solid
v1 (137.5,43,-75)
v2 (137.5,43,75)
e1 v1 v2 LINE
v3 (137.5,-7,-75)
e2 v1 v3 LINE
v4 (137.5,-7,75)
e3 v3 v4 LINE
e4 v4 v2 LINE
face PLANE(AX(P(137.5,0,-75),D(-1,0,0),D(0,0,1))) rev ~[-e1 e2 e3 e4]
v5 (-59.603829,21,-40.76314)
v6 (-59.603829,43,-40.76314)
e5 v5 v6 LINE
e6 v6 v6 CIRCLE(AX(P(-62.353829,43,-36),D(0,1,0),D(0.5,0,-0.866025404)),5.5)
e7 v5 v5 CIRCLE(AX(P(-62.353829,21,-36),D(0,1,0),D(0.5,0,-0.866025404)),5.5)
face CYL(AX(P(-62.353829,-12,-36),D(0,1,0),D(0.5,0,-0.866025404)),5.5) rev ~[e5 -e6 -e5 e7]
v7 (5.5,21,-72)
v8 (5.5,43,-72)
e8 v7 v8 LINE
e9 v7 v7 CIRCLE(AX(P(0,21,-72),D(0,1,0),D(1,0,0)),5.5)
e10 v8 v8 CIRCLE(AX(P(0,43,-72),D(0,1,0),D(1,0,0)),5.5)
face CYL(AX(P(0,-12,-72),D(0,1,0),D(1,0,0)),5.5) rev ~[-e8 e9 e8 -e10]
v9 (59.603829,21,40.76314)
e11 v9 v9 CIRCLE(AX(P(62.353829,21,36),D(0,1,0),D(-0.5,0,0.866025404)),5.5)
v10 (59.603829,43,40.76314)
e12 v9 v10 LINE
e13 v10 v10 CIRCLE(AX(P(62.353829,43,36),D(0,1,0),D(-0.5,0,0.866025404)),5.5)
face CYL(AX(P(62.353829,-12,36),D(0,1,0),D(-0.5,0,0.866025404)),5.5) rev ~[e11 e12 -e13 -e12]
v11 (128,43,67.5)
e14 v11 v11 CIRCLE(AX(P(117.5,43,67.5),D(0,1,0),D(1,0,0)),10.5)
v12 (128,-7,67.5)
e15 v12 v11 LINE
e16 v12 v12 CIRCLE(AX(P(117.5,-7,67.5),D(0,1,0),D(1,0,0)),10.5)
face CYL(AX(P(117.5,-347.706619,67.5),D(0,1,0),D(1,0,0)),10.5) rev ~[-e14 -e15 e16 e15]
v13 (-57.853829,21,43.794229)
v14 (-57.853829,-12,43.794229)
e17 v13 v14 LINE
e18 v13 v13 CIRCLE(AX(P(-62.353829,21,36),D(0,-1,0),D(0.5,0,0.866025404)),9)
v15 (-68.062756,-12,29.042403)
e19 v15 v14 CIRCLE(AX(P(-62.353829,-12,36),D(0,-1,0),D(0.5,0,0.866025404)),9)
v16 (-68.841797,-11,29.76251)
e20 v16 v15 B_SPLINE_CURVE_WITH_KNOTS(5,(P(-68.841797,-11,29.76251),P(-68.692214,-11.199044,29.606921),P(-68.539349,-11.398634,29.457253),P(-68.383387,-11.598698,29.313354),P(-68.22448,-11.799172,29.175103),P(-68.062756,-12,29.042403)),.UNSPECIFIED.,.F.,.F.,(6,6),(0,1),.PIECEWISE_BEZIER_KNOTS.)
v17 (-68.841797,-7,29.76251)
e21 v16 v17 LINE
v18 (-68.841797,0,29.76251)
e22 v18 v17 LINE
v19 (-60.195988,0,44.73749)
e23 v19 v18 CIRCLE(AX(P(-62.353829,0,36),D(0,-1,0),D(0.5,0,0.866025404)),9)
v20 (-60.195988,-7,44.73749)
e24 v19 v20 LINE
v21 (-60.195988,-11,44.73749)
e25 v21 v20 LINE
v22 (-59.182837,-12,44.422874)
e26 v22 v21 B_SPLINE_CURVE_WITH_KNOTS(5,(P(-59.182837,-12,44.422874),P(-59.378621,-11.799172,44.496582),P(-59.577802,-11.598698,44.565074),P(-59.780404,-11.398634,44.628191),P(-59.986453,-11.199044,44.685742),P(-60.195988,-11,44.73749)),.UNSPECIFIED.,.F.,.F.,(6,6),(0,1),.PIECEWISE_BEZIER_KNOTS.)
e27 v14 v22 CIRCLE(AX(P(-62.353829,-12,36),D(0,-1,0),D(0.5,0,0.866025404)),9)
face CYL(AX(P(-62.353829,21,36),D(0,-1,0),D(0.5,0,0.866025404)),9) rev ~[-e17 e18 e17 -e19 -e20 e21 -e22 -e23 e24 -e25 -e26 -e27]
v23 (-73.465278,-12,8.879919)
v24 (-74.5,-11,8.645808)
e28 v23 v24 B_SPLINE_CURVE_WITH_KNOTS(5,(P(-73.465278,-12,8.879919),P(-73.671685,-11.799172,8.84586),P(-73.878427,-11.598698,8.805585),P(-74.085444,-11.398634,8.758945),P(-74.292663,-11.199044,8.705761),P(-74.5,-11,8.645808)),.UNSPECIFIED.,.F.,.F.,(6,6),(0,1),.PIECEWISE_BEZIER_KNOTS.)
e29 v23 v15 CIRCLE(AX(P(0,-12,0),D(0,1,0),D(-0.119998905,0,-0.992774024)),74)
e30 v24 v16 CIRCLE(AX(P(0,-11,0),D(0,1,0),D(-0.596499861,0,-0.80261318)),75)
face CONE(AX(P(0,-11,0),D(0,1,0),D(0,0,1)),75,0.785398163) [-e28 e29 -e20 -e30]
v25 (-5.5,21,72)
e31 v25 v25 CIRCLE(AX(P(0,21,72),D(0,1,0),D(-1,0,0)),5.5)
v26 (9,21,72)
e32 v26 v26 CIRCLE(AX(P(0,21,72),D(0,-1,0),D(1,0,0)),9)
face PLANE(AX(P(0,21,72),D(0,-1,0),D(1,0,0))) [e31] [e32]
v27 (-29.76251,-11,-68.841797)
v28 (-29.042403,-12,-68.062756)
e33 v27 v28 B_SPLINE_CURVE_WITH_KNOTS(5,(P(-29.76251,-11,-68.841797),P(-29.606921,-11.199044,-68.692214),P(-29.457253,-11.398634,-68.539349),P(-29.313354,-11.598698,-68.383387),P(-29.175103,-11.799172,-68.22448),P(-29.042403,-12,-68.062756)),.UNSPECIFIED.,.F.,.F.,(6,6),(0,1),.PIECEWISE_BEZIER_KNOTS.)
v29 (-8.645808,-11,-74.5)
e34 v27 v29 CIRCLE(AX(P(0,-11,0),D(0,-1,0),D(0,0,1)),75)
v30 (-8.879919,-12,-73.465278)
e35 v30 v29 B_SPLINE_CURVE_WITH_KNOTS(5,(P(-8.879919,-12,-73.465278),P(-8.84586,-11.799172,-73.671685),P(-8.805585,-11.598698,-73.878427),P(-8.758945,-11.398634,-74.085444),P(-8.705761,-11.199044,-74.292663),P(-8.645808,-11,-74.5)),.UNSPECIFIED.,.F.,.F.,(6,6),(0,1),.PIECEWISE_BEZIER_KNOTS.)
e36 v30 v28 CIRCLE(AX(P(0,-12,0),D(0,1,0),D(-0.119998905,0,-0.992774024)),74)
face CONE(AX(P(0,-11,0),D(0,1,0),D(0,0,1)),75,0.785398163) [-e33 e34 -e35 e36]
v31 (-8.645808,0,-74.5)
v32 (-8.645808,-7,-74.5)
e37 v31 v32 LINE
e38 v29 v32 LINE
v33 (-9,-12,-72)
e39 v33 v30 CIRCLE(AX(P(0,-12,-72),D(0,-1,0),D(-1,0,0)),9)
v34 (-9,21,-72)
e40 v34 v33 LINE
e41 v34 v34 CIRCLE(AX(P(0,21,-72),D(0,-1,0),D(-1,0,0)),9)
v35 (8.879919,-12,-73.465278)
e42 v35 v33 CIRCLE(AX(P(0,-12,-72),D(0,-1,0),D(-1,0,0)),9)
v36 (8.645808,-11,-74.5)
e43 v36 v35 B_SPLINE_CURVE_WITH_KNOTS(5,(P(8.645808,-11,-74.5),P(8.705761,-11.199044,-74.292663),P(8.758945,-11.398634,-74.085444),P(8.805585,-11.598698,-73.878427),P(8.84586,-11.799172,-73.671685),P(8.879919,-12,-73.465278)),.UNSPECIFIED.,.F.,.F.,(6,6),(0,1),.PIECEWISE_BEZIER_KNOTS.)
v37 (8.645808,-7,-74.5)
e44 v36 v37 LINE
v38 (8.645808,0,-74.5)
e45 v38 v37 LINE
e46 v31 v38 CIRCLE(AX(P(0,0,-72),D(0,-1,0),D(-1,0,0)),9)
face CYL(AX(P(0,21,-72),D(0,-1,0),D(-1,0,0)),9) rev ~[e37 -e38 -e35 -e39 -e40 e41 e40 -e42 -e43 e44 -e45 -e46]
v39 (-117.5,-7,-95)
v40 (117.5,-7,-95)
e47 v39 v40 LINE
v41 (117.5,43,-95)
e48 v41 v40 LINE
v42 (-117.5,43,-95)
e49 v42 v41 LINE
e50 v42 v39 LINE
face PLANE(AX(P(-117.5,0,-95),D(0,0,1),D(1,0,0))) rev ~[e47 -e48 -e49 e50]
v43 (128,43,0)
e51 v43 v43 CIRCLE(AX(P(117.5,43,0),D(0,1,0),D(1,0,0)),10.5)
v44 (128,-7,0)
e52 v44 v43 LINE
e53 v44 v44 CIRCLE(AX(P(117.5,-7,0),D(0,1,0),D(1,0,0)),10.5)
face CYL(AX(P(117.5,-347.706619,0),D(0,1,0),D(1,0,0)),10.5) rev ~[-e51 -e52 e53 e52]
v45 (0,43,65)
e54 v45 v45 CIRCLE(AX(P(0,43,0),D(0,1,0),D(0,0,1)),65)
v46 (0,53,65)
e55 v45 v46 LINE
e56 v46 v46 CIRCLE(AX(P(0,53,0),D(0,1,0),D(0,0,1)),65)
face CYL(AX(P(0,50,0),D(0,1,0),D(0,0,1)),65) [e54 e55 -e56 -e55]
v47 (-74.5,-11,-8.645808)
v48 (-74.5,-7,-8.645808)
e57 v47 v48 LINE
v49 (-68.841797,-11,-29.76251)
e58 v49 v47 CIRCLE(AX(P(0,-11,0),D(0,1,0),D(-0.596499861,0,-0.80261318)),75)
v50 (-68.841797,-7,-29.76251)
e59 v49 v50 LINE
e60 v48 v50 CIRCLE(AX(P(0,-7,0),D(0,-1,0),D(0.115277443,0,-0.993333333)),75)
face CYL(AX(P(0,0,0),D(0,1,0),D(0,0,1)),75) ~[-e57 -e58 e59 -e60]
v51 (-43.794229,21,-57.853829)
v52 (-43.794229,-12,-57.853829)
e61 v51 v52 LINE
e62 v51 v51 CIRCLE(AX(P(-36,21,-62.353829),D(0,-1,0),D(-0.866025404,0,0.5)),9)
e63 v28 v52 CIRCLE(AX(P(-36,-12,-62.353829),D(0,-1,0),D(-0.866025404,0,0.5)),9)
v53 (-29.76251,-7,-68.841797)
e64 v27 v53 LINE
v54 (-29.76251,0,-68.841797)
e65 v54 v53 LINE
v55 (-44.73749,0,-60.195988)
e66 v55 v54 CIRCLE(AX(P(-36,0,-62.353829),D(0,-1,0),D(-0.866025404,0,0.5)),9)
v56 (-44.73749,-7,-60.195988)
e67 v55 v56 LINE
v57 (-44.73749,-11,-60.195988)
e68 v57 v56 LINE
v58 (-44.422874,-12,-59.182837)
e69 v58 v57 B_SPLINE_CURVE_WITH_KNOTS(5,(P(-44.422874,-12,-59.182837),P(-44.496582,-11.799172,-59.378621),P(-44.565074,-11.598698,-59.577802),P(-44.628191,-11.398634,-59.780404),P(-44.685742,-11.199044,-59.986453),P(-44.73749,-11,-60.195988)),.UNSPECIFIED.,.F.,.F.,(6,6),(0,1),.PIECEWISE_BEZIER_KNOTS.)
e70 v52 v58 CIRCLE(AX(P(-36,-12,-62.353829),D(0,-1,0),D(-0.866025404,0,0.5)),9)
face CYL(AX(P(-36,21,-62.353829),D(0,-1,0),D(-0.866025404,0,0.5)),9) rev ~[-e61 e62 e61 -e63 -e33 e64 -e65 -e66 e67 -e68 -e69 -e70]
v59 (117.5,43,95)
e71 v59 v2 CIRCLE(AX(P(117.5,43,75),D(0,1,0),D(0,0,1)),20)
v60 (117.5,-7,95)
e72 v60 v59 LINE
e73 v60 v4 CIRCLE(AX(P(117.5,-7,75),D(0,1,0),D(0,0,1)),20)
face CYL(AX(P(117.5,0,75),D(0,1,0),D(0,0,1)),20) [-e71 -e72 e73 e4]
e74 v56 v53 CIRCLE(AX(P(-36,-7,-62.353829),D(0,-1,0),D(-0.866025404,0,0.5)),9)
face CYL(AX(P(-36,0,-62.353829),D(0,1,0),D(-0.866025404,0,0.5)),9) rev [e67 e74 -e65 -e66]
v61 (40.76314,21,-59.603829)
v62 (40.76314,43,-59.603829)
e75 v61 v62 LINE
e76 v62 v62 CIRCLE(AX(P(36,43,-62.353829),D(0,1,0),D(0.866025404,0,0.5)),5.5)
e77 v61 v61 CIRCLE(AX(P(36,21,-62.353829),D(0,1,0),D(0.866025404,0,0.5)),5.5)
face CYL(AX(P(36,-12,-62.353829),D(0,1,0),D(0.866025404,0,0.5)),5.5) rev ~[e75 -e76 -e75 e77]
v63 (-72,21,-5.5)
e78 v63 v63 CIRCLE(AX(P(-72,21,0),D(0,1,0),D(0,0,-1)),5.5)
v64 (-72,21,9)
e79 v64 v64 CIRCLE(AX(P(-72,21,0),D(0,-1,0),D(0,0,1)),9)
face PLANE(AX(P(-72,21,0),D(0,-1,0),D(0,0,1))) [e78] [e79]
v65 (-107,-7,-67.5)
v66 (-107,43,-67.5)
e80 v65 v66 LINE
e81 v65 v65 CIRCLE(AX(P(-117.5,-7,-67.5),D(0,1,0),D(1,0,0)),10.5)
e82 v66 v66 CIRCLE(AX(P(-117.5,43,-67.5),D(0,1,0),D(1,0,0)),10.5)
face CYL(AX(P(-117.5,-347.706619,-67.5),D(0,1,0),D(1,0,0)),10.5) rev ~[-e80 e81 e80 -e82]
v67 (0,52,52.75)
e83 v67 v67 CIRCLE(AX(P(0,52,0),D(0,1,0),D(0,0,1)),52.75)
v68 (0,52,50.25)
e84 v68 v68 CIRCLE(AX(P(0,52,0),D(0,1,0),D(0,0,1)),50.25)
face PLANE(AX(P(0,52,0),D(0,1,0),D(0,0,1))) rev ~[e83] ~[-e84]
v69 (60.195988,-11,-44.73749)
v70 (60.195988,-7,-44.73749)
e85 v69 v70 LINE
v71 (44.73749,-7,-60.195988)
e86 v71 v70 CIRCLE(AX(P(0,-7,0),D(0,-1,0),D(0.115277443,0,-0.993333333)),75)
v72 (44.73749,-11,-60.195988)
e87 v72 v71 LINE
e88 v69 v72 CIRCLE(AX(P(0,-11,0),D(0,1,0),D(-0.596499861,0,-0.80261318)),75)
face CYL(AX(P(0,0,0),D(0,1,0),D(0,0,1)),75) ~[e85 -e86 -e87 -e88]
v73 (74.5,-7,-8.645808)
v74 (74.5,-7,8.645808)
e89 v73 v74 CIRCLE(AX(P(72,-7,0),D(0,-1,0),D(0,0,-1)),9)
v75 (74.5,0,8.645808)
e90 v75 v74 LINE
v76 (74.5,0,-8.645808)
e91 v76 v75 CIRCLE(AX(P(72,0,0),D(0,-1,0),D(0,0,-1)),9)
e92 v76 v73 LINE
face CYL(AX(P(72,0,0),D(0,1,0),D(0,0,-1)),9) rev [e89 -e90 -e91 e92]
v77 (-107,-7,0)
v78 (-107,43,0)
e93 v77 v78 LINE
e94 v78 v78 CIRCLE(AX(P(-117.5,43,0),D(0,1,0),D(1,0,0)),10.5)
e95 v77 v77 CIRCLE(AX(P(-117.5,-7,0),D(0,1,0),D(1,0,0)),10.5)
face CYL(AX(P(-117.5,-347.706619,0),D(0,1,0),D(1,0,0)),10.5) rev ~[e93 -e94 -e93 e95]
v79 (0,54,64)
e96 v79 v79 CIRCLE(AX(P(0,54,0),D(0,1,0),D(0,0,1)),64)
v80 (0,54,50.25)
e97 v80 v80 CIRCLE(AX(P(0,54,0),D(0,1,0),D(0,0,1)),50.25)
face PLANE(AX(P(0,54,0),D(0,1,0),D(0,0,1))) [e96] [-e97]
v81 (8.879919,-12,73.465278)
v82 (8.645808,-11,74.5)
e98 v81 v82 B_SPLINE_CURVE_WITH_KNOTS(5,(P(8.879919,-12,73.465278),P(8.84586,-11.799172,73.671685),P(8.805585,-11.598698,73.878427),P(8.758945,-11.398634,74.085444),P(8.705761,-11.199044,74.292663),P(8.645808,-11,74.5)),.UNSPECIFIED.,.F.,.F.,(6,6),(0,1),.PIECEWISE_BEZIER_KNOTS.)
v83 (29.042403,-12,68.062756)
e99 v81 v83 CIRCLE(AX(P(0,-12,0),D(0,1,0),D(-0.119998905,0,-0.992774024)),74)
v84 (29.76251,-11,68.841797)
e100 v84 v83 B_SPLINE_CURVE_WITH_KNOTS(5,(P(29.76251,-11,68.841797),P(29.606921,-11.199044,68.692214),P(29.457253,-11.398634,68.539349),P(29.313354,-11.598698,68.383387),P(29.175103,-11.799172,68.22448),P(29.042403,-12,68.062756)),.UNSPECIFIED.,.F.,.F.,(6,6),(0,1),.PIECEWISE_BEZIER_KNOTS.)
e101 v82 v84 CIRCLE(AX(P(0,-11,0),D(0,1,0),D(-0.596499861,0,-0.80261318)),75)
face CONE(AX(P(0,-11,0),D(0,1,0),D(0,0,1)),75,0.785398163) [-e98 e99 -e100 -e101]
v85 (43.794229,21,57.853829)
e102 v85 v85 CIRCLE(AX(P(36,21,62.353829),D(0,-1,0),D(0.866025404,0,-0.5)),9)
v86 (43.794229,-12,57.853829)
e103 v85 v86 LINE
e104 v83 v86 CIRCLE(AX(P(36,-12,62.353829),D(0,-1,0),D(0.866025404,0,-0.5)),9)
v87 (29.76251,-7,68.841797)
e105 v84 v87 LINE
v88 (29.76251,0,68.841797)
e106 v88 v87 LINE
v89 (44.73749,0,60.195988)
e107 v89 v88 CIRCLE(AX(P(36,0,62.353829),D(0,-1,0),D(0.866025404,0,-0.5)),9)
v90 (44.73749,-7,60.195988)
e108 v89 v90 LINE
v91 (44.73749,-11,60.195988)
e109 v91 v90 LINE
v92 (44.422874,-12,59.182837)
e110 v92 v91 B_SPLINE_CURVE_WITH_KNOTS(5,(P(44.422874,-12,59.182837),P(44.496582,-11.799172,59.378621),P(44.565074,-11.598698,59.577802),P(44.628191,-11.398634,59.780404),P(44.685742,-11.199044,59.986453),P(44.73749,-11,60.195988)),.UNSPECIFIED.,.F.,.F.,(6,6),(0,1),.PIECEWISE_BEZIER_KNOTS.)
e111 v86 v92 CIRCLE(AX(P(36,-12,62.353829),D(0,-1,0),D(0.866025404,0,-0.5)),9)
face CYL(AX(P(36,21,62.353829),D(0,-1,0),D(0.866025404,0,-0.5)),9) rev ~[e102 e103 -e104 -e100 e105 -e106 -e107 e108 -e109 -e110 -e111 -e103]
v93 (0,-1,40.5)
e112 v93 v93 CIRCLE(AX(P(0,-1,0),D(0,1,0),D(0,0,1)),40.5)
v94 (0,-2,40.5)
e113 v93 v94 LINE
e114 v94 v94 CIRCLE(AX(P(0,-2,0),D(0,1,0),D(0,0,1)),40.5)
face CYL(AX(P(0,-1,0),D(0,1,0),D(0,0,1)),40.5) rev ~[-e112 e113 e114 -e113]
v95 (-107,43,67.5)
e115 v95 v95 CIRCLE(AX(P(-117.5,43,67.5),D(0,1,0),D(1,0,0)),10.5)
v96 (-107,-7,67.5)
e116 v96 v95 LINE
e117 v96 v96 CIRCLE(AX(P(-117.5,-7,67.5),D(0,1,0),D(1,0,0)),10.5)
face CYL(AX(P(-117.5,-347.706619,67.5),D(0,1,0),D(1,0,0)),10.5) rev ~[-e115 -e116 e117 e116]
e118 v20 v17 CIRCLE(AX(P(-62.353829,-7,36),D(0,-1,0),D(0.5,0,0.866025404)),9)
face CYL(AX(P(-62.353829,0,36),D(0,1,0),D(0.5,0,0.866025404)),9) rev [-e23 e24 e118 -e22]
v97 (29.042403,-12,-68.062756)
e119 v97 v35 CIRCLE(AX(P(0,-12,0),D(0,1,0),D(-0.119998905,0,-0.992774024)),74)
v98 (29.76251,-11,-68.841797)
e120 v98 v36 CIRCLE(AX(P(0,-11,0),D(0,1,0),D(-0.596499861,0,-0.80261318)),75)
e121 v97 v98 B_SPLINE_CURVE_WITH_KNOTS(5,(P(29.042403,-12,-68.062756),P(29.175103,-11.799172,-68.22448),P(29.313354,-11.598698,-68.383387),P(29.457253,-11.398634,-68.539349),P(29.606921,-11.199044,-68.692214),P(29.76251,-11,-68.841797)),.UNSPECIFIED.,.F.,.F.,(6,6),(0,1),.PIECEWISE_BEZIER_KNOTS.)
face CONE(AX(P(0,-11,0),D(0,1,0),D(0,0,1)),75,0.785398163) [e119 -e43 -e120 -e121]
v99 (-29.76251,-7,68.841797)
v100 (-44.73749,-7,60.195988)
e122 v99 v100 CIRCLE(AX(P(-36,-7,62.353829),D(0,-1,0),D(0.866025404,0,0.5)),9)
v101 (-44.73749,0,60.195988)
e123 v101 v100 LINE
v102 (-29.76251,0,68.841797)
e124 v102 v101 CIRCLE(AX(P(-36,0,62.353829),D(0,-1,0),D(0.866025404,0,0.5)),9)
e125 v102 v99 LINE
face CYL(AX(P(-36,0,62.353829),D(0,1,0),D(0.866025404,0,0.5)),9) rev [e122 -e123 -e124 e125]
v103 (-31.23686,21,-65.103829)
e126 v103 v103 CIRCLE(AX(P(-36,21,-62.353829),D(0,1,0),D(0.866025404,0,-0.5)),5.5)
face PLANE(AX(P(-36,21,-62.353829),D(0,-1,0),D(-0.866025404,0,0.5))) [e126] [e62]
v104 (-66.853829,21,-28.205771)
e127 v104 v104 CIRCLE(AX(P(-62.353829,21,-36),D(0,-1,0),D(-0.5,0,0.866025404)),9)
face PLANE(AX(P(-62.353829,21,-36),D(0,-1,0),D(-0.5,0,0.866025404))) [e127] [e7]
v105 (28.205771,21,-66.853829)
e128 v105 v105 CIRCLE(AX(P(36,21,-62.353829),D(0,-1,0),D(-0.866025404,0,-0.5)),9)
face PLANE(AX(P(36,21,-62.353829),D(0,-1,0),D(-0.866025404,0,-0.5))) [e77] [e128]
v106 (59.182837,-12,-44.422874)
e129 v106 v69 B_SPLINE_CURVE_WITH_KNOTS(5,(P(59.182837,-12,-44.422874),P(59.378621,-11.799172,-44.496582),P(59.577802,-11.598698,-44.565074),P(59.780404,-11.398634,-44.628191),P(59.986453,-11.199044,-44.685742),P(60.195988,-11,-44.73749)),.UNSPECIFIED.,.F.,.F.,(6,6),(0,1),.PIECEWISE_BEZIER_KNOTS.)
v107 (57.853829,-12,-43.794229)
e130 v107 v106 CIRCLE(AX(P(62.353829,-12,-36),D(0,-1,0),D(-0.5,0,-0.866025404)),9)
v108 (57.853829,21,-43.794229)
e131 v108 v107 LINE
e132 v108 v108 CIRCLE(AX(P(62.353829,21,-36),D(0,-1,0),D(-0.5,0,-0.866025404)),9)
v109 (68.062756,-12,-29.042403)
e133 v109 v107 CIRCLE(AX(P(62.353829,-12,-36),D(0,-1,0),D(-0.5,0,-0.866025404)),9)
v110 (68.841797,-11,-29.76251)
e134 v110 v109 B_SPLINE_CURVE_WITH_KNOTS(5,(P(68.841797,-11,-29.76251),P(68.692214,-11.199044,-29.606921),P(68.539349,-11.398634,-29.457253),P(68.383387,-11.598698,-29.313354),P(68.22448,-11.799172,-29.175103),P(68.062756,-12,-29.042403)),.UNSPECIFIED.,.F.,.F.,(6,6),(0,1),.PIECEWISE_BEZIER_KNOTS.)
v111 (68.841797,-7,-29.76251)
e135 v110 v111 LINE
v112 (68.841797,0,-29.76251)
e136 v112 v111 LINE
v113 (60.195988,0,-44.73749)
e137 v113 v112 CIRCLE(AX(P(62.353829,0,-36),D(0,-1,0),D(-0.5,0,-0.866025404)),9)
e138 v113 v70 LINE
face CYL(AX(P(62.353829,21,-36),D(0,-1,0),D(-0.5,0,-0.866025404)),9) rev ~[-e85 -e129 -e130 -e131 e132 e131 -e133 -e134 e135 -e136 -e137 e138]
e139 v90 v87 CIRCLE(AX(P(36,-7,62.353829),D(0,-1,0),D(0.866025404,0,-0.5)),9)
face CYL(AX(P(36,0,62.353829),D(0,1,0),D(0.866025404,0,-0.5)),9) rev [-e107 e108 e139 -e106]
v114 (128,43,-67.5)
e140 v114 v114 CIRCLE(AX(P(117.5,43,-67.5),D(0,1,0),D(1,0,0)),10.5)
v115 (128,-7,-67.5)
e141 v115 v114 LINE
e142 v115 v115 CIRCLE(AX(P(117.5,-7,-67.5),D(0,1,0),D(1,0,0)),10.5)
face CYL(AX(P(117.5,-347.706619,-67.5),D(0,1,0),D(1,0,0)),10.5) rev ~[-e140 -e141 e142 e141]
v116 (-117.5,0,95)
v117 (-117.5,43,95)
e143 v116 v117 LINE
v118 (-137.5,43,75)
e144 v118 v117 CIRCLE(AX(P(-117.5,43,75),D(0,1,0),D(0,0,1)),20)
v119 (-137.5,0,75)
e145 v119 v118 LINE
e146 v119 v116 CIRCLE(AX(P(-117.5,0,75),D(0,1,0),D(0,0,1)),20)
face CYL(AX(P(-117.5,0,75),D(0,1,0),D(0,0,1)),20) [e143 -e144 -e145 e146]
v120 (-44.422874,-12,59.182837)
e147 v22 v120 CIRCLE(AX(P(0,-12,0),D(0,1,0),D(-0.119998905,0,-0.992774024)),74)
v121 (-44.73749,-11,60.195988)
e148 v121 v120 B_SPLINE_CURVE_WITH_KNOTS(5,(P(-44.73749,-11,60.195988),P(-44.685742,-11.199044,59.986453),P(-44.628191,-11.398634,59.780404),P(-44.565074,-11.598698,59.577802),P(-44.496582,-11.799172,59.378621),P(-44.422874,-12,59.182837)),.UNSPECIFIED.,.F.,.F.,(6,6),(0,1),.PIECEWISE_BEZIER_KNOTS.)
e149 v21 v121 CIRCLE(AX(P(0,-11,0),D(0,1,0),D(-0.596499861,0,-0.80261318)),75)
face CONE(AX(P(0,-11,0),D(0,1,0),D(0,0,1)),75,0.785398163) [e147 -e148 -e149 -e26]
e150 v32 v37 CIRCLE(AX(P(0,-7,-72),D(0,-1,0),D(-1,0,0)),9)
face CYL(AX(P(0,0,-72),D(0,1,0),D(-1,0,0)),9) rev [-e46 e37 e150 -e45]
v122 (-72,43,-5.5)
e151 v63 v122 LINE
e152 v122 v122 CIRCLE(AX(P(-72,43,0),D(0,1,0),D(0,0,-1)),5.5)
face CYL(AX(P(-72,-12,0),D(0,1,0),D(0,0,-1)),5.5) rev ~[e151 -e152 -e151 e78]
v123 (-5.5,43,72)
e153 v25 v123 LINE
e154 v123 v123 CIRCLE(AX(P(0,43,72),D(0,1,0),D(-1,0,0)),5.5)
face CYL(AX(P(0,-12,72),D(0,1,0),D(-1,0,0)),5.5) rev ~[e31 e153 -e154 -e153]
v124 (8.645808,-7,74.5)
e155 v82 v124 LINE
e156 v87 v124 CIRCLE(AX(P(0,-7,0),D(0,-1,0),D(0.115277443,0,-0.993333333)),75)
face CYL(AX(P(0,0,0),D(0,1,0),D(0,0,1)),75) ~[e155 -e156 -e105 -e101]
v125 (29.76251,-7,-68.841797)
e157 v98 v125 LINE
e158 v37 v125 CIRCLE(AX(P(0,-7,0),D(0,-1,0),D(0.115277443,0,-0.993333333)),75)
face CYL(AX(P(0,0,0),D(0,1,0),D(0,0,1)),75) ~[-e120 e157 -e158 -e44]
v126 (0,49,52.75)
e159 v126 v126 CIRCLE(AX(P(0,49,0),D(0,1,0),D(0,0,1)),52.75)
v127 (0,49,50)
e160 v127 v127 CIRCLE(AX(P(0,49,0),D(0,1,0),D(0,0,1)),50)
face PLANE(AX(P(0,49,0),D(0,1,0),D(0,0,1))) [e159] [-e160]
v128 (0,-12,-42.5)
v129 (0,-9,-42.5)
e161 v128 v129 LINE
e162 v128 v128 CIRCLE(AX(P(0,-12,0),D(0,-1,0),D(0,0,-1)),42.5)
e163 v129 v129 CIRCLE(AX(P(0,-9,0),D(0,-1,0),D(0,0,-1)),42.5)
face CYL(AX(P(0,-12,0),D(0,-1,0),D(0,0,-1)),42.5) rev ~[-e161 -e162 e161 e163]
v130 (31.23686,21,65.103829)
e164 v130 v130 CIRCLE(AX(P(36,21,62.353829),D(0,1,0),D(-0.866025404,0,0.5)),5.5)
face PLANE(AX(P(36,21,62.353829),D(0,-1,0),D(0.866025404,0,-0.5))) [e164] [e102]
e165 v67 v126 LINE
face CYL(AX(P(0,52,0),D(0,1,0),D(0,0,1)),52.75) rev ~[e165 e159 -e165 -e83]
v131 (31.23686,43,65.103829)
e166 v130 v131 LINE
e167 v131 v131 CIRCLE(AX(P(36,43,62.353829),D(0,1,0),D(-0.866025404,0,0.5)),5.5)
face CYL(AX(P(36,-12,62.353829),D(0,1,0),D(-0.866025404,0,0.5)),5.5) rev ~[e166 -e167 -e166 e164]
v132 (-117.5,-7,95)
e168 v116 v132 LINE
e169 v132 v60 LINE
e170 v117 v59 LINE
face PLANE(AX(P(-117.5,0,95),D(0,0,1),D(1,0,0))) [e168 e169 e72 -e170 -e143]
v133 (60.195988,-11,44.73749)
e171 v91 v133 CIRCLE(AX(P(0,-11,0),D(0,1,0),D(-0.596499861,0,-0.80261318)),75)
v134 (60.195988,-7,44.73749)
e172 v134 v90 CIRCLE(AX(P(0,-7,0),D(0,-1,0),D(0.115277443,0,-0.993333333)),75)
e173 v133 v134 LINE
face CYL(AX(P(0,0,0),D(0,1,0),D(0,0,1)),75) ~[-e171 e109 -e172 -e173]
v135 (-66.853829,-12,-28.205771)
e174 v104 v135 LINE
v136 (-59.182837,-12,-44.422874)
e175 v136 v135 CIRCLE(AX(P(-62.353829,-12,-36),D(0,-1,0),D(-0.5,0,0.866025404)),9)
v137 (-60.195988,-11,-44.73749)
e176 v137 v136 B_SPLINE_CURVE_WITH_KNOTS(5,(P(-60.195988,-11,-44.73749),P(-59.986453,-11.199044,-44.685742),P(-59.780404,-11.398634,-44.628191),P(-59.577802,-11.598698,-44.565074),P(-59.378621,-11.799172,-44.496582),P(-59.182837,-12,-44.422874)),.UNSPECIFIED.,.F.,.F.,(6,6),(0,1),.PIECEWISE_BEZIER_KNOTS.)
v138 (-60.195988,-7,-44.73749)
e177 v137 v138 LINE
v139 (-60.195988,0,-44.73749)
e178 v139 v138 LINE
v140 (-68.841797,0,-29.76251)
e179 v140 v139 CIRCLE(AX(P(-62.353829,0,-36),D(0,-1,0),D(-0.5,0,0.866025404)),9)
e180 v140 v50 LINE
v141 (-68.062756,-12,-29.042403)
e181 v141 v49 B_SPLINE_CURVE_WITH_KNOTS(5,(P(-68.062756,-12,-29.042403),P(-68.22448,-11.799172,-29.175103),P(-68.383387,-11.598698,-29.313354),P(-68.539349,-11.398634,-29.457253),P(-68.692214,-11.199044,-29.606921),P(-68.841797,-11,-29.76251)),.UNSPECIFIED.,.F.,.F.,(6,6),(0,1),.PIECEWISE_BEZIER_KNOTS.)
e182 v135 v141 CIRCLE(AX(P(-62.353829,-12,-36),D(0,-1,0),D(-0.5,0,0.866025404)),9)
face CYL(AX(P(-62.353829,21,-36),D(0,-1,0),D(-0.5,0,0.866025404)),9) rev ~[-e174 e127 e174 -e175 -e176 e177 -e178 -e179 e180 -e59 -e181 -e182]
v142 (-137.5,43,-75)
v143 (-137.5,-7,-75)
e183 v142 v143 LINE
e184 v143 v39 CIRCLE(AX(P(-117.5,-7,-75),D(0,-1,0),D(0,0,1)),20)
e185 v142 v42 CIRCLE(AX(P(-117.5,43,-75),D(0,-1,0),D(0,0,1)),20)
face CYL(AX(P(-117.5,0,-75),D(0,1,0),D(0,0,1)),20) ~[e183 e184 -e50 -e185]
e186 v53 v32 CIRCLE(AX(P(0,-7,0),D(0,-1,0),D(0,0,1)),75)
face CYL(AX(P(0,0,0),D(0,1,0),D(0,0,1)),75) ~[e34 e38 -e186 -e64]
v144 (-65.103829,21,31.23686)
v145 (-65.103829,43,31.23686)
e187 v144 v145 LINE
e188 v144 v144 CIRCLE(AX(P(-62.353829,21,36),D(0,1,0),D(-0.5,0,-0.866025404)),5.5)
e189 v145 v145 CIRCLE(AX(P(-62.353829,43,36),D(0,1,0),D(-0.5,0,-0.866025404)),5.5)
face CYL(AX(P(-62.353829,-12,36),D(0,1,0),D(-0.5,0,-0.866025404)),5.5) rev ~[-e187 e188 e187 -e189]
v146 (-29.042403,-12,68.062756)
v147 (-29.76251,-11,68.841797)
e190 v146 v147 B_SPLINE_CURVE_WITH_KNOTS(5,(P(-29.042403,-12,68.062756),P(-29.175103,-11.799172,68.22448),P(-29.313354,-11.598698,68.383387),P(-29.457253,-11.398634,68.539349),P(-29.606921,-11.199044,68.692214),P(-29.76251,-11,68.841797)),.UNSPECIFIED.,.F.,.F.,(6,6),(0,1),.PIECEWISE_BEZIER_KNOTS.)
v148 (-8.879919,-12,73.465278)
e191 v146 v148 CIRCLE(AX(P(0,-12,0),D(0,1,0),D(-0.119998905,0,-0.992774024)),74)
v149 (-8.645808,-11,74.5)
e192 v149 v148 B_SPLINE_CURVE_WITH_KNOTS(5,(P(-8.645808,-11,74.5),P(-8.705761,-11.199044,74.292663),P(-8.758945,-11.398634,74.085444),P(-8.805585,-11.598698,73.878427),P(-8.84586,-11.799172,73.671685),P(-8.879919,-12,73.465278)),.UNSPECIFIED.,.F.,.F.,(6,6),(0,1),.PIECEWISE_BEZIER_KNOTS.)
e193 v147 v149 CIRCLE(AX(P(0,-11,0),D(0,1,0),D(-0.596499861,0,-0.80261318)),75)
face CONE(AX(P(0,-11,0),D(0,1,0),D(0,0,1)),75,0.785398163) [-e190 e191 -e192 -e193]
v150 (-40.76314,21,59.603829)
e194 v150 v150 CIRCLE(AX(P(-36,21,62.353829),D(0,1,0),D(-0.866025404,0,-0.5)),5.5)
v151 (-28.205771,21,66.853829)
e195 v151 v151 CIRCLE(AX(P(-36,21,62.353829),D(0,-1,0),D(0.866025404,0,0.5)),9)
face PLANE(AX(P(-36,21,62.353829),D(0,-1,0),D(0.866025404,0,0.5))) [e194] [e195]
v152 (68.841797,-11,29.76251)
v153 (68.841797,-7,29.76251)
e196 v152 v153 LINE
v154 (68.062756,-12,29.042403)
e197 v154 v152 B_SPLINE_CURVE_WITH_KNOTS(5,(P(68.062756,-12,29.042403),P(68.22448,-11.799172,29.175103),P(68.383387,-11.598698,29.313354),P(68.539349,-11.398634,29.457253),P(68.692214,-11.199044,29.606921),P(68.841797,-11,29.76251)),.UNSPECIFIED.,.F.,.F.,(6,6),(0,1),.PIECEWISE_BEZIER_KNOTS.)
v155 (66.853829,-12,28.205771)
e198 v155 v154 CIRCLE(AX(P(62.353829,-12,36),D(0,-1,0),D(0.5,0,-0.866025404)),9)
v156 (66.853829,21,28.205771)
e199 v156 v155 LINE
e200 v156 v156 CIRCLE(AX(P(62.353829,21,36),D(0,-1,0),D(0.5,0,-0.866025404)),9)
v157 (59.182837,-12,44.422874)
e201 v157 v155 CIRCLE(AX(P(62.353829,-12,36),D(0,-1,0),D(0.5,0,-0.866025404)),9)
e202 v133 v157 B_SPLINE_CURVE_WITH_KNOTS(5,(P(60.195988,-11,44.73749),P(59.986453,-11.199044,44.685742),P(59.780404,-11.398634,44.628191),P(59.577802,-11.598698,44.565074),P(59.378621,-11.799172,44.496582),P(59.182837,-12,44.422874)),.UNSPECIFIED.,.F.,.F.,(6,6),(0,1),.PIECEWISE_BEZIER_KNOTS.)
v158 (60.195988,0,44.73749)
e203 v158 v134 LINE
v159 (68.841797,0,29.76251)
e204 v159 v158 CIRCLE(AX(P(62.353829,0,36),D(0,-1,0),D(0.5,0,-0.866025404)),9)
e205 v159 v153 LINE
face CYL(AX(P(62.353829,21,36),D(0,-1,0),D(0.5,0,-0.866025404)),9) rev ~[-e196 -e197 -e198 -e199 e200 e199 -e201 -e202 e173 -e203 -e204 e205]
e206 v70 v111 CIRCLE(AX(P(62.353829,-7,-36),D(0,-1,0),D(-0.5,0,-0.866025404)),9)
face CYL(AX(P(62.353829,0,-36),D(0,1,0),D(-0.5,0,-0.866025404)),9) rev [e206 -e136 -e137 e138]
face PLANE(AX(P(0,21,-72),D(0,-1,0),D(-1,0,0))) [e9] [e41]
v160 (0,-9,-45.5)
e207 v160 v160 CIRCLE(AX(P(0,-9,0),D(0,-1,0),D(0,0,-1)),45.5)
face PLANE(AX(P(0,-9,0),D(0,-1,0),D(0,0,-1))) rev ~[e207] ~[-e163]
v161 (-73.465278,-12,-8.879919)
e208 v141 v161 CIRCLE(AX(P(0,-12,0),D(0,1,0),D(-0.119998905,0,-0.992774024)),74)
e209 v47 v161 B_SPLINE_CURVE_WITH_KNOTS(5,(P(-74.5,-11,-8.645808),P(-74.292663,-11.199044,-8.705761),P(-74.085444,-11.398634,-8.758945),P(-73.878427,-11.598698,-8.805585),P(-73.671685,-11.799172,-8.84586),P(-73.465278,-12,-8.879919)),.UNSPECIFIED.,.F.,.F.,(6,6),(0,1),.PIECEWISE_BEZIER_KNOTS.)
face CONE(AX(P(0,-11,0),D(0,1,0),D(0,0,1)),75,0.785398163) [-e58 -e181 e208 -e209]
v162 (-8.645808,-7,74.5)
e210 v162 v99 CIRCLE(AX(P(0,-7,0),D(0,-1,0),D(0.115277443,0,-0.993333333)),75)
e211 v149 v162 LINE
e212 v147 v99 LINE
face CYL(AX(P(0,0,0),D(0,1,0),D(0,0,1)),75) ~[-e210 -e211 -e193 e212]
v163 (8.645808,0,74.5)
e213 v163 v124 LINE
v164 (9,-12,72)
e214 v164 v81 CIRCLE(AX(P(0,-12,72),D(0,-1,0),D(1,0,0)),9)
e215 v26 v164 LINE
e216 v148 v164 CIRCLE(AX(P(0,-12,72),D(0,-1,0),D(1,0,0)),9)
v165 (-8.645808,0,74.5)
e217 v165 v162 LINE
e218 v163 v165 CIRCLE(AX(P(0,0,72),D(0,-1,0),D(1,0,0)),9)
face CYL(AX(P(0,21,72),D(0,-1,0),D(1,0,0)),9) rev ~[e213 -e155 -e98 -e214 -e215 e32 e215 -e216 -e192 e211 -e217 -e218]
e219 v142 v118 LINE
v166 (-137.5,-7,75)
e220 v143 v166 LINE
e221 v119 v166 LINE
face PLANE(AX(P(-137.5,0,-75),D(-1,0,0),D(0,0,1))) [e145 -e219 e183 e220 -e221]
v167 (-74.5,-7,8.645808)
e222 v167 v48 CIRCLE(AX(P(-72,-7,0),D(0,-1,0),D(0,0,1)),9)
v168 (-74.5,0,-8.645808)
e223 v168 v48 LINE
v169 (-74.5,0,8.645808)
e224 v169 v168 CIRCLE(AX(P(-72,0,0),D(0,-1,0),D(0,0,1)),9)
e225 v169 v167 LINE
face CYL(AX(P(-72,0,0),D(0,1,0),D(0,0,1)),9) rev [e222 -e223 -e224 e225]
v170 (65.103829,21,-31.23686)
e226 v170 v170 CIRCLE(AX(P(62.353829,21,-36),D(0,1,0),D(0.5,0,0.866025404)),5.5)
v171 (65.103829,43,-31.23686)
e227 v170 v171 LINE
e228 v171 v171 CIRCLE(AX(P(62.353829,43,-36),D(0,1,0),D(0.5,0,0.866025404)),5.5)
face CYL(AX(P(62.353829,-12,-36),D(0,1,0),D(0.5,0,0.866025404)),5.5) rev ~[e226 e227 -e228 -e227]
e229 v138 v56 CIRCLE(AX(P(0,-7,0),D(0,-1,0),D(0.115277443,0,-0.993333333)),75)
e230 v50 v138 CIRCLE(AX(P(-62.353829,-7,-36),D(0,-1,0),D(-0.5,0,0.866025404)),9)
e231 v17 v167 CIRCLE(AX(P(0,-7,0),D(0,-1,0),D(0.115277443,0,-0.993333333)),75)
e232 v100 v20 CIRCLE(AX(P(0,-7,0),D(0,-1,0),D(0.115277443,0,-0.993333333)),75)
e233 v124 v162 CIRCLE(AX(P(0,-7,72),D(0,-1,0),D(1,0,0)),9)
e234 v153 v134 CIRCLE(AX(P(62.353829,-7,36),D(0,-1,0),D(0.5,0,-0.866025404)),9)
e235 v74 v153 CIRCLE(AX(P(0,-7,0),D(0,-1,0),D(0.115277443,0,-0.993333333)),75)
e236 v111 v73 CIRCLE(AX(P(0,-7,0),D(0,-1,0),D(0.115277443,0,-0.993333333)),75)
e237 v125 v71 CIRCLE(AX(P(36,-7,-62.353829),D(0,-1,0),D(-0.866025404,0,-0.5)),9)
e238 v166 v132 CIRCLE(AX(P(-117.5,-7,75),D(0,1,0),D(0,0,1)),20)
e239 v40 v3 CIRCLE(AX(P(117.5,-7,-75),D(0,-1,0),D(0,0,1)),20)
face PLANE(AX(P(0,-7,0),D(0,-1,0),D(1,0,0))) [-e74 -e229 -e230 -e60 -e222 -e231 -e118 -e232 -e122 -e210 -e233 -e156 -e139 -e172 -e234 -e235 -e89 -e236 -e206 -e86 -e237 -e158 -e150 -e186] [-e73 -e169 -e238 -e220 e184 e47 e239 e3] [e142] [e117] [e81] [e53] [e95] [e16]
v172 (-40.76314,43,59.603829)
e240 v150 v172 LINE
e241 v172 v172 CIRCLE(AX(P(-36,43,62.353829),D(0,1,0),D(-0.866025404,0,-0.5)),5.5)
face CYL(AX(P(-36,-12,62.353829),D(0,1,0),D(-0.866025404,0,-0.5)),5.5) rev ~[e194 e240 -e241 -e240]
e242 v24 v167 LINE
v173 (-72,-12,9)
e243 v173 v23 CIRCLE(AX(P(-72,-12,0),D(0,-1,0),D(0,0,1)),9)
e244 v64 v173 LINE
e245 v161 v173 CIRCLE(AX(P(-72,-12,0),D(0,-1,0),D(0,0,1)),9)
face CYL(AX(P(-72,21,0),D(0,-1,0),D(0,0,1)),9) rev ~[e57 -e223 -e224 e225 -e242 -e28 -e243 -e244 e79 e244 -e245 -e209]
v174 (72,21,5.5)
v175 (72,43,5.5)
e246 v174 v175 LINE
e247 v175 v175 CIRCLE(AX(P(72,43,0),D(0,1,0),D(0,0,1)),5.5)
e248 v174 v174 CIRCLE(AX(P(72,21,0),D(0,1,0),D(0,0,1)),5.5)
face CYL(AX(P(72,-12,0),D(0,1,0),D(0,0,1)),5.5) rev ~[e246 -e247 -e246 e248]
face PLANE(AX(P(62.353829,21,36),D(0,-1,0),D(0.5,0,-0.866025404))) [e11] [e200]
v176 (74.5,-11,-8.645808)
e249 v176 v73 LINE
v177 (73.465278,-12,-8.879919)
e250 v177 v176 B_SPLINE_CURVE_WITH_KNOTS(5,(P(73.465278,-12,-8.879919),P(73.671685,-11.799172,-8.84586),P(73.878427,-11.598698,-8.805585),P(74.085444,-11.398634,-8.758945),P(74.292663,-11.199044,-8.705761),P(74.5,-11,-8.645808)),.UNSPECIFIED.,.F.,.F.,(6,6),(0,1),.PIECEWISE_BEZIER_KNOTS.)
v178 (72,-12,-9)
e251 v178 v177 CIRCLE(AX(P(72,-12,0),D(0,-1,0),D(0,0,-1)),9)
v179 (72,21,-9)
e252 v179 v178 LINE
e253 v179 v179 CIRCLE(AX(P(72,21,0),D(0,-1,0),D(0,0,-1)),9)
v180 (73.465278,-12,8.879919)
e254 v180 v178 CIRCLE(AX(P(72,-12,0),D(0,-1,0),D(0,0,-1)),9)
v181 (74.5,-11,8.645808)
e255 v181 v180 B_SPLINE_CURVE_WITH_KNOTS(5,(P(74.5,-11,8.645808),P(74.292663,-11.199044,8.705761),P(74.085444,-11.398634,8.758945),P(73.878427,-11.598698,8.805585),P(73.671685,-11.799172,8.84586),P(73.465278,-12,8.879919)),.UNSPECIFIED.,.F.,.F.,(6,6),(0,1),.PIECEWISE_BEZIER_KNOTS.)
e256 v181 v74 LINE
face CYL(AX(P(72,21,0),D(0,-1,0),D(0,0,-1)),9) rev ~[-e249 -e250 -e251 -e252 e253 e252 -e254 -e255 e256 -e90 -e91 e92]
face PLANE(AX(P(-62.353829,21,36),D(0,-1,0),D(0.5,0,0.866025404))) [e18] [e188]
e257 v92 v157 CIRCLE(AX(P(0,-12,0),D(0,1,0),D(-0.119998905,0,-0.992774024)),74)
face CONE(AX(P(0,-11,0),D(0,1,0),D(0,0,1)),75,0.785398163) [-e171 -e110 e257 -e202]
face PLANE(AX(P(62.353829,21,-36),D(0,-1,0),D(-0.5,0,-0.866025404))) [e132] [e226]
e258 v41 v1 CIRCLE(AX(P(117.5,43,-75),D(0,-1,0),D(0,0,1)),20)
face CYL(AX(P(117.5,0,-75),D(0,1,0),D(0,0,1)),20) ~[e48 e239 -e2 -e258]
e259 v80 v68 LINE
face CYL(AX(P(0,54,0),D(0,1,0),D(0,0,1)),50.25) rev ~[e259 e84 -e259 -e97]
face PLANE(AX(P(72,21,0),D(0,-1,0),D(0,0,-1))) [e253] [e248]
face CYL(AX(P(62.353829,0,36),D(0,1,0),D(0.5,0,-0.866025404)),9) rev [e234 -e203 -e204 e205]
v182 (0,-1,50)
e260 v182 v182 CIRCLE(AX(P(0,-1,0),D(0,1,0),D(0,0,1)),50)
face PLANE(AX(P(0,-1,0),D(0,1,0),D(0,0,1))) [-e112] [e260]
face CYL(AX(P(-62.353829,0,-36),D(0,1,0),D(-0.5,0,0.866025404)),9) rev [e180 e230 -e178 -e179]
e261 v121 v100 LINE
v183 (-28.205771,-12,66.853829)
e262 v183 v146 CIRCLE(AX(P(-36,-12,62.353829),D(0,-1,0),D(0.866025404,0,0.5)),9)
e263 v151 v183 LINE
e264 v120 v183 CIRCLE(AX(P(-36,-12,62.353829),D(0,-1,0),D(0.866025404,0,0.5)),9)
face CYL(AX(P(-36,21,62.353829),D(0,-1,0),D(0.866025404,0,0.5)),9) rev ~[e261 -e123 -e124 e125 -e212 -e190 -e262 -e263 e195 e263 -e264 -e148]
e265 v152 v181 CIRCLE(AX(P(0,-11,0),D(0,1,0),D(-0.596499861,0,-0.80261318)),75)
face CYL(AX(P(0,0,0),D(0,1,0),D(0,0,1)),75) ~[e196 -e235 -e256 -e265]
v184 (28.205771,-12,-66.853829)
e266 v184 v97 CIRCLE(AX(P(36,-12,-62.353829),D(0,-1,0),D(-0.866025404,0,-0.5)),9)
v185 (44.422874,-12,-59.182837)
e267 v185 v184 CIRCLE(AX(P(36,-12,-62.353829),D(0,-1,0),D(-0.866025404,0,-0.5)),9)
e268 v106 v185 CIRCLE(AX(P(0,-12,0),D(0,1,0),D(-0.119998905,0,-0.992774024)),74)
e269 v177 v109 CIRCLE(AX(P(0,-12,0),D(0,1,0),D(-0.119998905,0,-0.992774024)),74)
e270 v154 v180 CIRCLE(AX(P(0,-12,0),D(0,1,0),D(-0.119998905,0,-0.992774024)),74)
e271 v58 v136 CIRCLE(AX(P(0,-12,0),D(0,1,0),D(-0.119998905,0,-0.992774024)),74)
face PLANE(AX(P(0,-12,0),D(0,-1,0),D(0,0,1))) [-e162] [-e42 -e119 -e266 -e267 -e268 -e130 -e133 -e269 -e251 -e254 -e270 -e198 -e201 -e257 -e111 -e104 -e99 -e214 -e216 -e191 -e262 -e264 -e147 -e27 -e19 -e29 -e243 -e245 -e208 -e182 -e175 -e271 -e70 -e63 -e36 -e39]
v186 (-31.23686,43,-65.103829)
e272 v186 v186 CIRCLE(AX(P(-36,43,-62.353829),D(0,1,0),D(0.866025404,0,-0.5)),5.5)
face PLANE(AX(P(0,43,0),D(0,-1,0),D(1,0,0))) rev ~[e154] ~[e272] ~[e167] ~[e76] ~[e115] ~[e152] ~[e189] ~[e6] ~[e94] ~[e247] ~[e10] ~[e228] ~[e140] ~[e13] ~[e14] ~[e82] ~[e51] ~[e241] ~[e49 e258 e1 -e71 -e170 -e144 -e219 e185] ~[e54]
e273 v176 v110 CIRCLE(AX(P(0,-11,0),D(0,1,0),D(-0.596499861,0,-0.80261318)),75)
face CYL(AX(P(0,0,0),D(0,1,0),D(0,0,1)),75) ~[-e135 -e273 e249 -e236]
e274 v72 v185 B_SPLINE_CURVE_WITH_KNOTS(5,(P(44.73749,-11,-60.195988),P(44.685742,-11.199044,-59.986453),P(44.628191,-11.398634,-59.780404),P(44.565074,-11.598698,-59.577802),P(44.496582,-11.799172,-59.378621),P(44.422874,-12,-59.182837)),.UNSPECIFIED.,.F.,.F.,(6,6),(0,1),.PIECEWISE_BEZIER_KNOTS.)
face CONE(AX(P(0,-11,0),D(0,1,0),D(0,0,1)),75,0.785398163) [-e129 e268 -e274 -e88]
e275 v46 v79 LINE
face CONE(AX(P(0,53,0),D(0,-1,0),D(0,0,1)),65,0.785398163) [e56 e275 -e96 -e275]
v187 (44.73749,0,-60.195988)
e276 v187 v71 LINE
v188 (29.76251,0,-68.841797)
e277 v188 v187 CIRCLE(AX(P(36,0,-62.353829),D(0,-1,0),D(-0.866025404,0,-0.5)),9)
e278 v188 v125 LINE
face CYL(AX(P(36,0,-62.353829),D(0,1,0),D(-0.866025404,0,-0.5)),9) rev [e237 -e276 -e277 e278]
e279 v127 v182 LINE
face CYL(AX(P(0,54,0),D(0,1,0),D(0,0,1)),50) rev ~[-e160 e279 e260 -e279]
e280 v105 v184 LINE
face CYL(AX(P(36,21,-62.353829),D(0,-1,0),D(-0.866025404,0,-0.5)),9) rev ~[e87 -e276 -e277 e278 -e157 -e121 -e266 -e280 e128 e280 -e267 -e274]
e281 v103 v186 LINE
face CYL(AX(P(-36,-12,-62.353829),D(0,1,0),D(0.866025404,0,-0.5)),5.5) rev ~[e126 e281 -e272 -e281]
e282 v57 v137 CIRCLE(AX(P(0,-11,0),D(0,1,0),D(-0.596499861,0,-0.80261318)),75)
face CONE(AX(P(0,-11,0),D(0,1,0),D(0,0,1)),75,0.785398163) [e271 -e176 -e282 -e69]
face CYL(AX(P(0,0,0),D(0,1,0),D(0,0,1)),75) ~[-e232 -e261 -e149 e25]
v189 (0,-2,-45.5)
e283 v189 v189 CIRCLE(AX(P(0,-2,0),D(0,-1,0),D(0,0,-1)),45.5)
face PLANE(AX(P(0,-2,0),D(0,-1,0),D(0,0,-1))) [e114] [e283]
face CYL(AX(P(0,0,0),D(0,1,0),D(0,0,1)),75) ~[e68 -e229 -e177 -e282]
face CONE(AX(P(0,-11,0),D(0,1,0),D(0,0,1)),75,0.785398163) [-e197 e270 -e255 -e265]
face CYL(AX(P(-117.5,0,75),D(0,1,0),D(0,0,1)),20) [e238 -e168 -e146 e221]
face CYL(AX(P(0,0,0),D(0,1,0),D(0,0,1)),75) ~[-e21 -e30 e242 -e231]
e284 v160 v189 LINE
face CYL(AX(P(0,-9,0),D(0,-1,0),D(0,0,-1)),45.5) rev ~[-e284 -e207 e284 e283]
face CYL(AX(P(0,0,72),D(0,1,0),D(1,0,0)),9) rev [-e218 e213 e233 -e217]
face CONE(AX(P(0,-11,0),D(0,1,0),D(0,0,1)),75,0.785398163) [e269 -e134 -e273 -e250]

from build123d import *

# Parameters (mm, degrees)
SKETCH1_R                                            = 102.5
BOSS_EXTRUDE1_DEPTH                                  = 50
SKETCH2_R                                            = 65
BOSS_EXTRUDE2_DEPTH                                  = 4
SKETCH3_R                                            = 75
BOSS_EXTRUDE3_DEPTH                                  = 12
CHAMFER1_SIZE                                        = 1
SKETCH4_R                                            = 50
CUT_EXTRUDE1_DEPTH                                   = 55
SKETCH5_R                                            = 40.5
CUT_EXTRUDE2_DEPTH                                   = 156.040317337
CUT_EXTRUDE3_START                                   = -3
SKETCH6_R                                            = 45.5
CUT_EXTRUDE3_DEPTH                                   = 7
SKETCH7_R                                            = 42.5
CUT_EXTRUDE4_DEPTH                                   = 5
CUT_EXTRUDE5_START                                   = -2
SKETCH8_R                                            = 52.75
CUT_EXTRUDE5_DEPTH                                   = 3
SKETCH9_R                                            = 50.25
CUT_EXTRUDE6_DEPTH                                   = 4
HOLE_SIZE_PER_SOCKET_HEAD_CAP_SCREW_TYPE_D           = 11
HOLE_SIZE_PER_SOCKET_HEAD_CAP_SCREW_TYPE_CBORE_D     = 18
HOLE_SIZE_PER_SOCKET_HEAD_CAP_SCREW_TYPE_CBORE_DEPTH = 33
CIRPATTERN1_COUNT                                    = 12
SKETCH14_OUTSIDE_W                                   = 266.466
SKETCH14_OUTSIDE_H                                   = 266.466
SKETCH14_OUTSIDE_R                                   = 82.5
CUT_EXTRUDE7_DEPTH                                   = 20
CHAMFER4_SIZE                                        = 1.5
SKETCH17_R                                           = 5.5
CUT_EXTRUDE11_DEPTH                                  = 151.918852396
CIRPATTERN4_COUNT                                    = 10
M12_TAPPED_HOLE1_D                                   = 10.2
SKETCH22_OUTSIDE_W                                   = 266.466
SKETCH22_OUTSIDE_H                                   = 266.466
SKETCH22_OUTSIDE_R                                   = 82.5
CUT_EXTRUDE12_DEPTH                                  = 155.688396462
SKETCH24_W                                           = 275
SKETCH24_H                                           = 190
SKETCH24_R                                           = 82.5
BOSS_EXTRUDE4_DEPTH                                  = 50
FILLET1_R                                            = 20
MOVE_FACE1_BY                                        = 7
MOVE_FACE2_BY                                        = 7
F_21_0_21_DIAMETER_HOLE1_D                           = 21


with BuildPart() as part:
    # Sketch1 → Boss-Extrude1 (new body)
    with BuildSketch(Plane(origin=(0, 0, 0), x_dir=(1, 0, 0), z_dir=(0, 1, 0))):
        with Locations(Location((0, 0, 0), (0, 0, 270))):
            Circle(SKETCH1_R)
    extrude(amount=BOSS_EXTRUDE1_DEPTH)

    # Sketch2 → Boss-Extrude2 (add)
    with BuildSketch(Plane(origin=(0, 50, 0), x_dir=(1, 0, 0), z_dir=(0, 1, 0))):
        with Locations(Location((0, 0, 0), (0, 0, 270))):
            Circle(SKETCH2_R)
    extrude(amount=BOSS_EXTRUDE2_DEPTH)

    # Sketch3 → Boss-Extrude3 (add)
    with BuildSketch(Plane.XZ):
        with Locations(Location((0, 0, 0), (0, 0, 90))):
            Circle(SKETCH3_R)
    extrude(amount=BOSS_EXTRUDE3_DEPTH)

    # Chamfer1
    chamfer1_edges = [part.edges().sort_by_distance(p)[0] for p in [
        (0, -12, -75),
        (0, 54, -65),
    ]]
    chamfer(chamfer1_edges, length=CHAMFER1_SIZE)

    # Sketch4 → Cut-Extrude1 (cut)
    with BuildSketch(Plane(origin=(0, 54, 0), x_dir=(1, 0, 0), z_dir=(0, 1, 0))):
        with Locations(Location((0, 0, 0), (0, 0, 270))):
            Circle(SKETCH4_R)
    extrude(amount=-CUT_EXTRUDE1_DEPTH, mode=Mode.SUBTRACT)

    # Sketch5 → Cut-Extrude2 (cut, through all)
    with BuildSketch(Plane(origin=(0, -1, 0), x_dir=(1, 0, 0), z_dir=(0, 1, 0))):
        with Locations(Location((0, 0, 0), (0, 0, 270))):
            Circle(SKETCH5_R)
    extrude(amount=-CUT_EXTRUDE2_DEPTH, mode=Mode.SUBTRACT)

    # Sketch6 → Cut-Extrude3 (cut)
    with BuildSketch(Plane.XZ.offset(12).offset(CUT_EXTRUDE3_START)):
        with Locations(Location((0, 0, 0), (0, 0, 270))):
            Circle(SKETCH6_R)
    extrude(amount=-CUT_EXTRUDE3_DEPTH, mode=Mode.SUBTRACT)

    # Sketch7 → Cut-Extrude4 (cut)
    with BuildSketch(Plane.XZ.offset(12)):
        with Locations(Location((0, 0, 0), (0, 0, 270))):
            Circle(SKETCH7_R)
    extrude(amount=-CUT_EXTRUDE4_DEPTH, mode=Mode.SUBTRACT)

    # Sketch8 → Cut-Extrude5 (cut)
    with BuildSketch(Plane(origin=(0, 54, 0), x_dir=(1, 0, 0), z_dir=(0, 1, 0)).offset(CUT_EXTRUDE5_START)):
        with Locations(Location((0, 0, 0), (0, 0, 270))):
            Circle(SKETCH8_R)
    extrude(amount=-CUT_EXTRUDE5_DEPTH, mode=Mode.SUBTRACT)

    # Sketch9 → Cut-Extrude6 (cut)
    with BuildSketch(Plane(origin=(0, 54, 0), x_dir=(1, 0, 0), z_dir=(0, 1, 0))):
        with Locations(Location((0, 0, 0), (0, 0, 270))):
            Circle(SKETCH9_R)
    extrude(amount=-CUT_EXTRUDE6_DEPTH, mode=Mode.SUBTRACT)

    # Hole Size per Socket Head Cap Screw Type1 (through all)
    with Locations(Plane(origin=(0, -12, 0), x_dir=(-1, 0, 0), z_dir=(0, -1, 0))):
        with Locations((0, 72)):
            hole_size_per_socket_head_cap_screw_type = CounterBoreHole(HOLE_SIZE_PER_SOCKET_HEAD_CAP_SCREW_TYPE_D / 2, HOLE_SIZE_PER_SOCKET_HEAD_CAP_SCREW_TYPE_CBORE_D / 2, HOLE_SIZE_PER_SOCKET_HEAD_CAP_SCREW_TYPE_CBORE_DEPTH)

    # CirPattern1: Hole Size per Socket Head Cap Screw Type1 ×12 about axis
    cirpattern1_axis = Axis((0, 0, 0), (0, 1, 0))
    for i in range(1, CIRPATTERN1_COUNT):
        add(hole_size_per_socket_head_cap_screw_type.rotate(cirpattern1_axis, i * 360 / CIRPATTERN1_COUNT), mode=Mode.SUBTRACT)

    # Sketch14 outside → Cut-Extrude7 (cut)
    with BuildSketch(Plane(origin=(0, 50, 0), x_dir=(1, 0, 0), z_dir=(0, 1, 0))):
        Rectangle(SKETCH14_OUTSIDE_W, SKETCH14_OUTSIDE_H)
        with Locations(Location((0, 0, 0), (0, 0, 270))):
            Circle(SKETCH14_OUTSIDE_R, mode=Mode.SUBTRACT)
    extrude(amount=-CUT_EXTRUDE7_DEPTH, mode=Mode.SUBTRACT)

    # Chamfer4
    chamfer4_edges = [part.edges().sort_by_distance(p)[0] for p in [
        (0, 0, -102.5),
        (0, 30, -102.5),
    ]]
    chamfer(chamfer4_edges, length=CHAMFER4_SIZE)

    # Sketch17 → Cut-Extrude11 (cut, through all)
    with BuildSketch(Plane(origin=(0, 30, 0), x_dir=(1, 0, 0), z_dir=(0, 1, 0))):
        with Locations(Location((92.5, 0, 0), (0, 0, 270))):
            Circle(SKETCH17_R)
    cut_extrude11 = extrude(amount=-CUT_EXTRUDE11_DEPTH, mode=Mode.SUBTRACT)

    # CirPattern4: Cut-Extrude11 ×10 about axis
    cirpattern4_axis = Axis((0, 0, 0), (0, 1, 0))
    for i in range(1, CIRPATTERN4_COUNT):
        add(cut_extrude11.rotate(cirpattern4_axis, i * 360 / CIRPATTERN4_COUNT), mode=Mode.SUBTRACT)

    # M12 Tapped Hole1 (through all)
    with Locations(Plane(origin=(0, 0, 0), x_dir=(-1, 0, 0), z_dir=(0, -1, 0))):
        with Locations((-87.972727757, 28.58407198)):
            Hole(M12_TAPPED_HOLE1_D / 2)

    # Sketch22 outside → Cut-Extrude12 (cut, through all)
    with BuildSketch(Plane.XZ):
        Rectangle(SKETCH22_OUTSIDE_W, SKETCH22_OUTSIDE_H)
        with Locations(Location((0, 0, 0), (0, 0, 90))):
            Circle(SKETCH22_OUTSIDE_R, mode=Mode.SUBTRACT)
    extrude(amount=-CUT_EXTRUDE12_DEPTH, mode=Mode.SUBTRACT)

    # Sketch24 → Boss-Extrude4 (add)
    with BuildSketch(Plane.XZ):
        Rectangle(SKETCH24_W, SKETCH24_H)
        Circle(SKETCH24_R, mode=Mode.SUBTRACT)
    extrude(amount=-BOSS_EXTRUDE4_DEPTH)

    # Fillet1
    fillet1_edges = [part.edges().sort_by_distance(p)[0] for p in [
        (-137.5, 25, -95),
        (-137.5, 25, 95),
        (137.5, 25, 95),
        (137.5, 25, -95),
    ]]
    fillet(fillet1_edges, radius=FILLET1_R)

    # Move Face1: a face moved outward by 7.0
    extrude(part.faces().sort_by_distance((-68.75, 0, 47.5))[0], amount=MOVE_FACE1_BY, dir=(0, -1, 0))

    # Move Face2: a face moved inward by 7.0
    extrude(part.faces().sort_by_distance((68.75, 50, -47.5))[0], amount=MOVE_FACE2_BY, dir=(0, -1, 0), mode=Mode.SUBTRACT)

    # Ø21.0 (21) Diameter Hole1 (through all)
    with Locations(Plane(origin=(0, -7, 0), x_dir=(-1, 0, 0), z_dir=(0, -1, 0))):
        with Locations((-117.5, 67.5), (-117.5, 0), (-117.5, -67.5), (117.5, 67.5), (117.5, 0), (117.5, -67.5)):
            Hole(F_21_0_21_DIAMETER_HOLE1_D / 2)


solid = part.part
